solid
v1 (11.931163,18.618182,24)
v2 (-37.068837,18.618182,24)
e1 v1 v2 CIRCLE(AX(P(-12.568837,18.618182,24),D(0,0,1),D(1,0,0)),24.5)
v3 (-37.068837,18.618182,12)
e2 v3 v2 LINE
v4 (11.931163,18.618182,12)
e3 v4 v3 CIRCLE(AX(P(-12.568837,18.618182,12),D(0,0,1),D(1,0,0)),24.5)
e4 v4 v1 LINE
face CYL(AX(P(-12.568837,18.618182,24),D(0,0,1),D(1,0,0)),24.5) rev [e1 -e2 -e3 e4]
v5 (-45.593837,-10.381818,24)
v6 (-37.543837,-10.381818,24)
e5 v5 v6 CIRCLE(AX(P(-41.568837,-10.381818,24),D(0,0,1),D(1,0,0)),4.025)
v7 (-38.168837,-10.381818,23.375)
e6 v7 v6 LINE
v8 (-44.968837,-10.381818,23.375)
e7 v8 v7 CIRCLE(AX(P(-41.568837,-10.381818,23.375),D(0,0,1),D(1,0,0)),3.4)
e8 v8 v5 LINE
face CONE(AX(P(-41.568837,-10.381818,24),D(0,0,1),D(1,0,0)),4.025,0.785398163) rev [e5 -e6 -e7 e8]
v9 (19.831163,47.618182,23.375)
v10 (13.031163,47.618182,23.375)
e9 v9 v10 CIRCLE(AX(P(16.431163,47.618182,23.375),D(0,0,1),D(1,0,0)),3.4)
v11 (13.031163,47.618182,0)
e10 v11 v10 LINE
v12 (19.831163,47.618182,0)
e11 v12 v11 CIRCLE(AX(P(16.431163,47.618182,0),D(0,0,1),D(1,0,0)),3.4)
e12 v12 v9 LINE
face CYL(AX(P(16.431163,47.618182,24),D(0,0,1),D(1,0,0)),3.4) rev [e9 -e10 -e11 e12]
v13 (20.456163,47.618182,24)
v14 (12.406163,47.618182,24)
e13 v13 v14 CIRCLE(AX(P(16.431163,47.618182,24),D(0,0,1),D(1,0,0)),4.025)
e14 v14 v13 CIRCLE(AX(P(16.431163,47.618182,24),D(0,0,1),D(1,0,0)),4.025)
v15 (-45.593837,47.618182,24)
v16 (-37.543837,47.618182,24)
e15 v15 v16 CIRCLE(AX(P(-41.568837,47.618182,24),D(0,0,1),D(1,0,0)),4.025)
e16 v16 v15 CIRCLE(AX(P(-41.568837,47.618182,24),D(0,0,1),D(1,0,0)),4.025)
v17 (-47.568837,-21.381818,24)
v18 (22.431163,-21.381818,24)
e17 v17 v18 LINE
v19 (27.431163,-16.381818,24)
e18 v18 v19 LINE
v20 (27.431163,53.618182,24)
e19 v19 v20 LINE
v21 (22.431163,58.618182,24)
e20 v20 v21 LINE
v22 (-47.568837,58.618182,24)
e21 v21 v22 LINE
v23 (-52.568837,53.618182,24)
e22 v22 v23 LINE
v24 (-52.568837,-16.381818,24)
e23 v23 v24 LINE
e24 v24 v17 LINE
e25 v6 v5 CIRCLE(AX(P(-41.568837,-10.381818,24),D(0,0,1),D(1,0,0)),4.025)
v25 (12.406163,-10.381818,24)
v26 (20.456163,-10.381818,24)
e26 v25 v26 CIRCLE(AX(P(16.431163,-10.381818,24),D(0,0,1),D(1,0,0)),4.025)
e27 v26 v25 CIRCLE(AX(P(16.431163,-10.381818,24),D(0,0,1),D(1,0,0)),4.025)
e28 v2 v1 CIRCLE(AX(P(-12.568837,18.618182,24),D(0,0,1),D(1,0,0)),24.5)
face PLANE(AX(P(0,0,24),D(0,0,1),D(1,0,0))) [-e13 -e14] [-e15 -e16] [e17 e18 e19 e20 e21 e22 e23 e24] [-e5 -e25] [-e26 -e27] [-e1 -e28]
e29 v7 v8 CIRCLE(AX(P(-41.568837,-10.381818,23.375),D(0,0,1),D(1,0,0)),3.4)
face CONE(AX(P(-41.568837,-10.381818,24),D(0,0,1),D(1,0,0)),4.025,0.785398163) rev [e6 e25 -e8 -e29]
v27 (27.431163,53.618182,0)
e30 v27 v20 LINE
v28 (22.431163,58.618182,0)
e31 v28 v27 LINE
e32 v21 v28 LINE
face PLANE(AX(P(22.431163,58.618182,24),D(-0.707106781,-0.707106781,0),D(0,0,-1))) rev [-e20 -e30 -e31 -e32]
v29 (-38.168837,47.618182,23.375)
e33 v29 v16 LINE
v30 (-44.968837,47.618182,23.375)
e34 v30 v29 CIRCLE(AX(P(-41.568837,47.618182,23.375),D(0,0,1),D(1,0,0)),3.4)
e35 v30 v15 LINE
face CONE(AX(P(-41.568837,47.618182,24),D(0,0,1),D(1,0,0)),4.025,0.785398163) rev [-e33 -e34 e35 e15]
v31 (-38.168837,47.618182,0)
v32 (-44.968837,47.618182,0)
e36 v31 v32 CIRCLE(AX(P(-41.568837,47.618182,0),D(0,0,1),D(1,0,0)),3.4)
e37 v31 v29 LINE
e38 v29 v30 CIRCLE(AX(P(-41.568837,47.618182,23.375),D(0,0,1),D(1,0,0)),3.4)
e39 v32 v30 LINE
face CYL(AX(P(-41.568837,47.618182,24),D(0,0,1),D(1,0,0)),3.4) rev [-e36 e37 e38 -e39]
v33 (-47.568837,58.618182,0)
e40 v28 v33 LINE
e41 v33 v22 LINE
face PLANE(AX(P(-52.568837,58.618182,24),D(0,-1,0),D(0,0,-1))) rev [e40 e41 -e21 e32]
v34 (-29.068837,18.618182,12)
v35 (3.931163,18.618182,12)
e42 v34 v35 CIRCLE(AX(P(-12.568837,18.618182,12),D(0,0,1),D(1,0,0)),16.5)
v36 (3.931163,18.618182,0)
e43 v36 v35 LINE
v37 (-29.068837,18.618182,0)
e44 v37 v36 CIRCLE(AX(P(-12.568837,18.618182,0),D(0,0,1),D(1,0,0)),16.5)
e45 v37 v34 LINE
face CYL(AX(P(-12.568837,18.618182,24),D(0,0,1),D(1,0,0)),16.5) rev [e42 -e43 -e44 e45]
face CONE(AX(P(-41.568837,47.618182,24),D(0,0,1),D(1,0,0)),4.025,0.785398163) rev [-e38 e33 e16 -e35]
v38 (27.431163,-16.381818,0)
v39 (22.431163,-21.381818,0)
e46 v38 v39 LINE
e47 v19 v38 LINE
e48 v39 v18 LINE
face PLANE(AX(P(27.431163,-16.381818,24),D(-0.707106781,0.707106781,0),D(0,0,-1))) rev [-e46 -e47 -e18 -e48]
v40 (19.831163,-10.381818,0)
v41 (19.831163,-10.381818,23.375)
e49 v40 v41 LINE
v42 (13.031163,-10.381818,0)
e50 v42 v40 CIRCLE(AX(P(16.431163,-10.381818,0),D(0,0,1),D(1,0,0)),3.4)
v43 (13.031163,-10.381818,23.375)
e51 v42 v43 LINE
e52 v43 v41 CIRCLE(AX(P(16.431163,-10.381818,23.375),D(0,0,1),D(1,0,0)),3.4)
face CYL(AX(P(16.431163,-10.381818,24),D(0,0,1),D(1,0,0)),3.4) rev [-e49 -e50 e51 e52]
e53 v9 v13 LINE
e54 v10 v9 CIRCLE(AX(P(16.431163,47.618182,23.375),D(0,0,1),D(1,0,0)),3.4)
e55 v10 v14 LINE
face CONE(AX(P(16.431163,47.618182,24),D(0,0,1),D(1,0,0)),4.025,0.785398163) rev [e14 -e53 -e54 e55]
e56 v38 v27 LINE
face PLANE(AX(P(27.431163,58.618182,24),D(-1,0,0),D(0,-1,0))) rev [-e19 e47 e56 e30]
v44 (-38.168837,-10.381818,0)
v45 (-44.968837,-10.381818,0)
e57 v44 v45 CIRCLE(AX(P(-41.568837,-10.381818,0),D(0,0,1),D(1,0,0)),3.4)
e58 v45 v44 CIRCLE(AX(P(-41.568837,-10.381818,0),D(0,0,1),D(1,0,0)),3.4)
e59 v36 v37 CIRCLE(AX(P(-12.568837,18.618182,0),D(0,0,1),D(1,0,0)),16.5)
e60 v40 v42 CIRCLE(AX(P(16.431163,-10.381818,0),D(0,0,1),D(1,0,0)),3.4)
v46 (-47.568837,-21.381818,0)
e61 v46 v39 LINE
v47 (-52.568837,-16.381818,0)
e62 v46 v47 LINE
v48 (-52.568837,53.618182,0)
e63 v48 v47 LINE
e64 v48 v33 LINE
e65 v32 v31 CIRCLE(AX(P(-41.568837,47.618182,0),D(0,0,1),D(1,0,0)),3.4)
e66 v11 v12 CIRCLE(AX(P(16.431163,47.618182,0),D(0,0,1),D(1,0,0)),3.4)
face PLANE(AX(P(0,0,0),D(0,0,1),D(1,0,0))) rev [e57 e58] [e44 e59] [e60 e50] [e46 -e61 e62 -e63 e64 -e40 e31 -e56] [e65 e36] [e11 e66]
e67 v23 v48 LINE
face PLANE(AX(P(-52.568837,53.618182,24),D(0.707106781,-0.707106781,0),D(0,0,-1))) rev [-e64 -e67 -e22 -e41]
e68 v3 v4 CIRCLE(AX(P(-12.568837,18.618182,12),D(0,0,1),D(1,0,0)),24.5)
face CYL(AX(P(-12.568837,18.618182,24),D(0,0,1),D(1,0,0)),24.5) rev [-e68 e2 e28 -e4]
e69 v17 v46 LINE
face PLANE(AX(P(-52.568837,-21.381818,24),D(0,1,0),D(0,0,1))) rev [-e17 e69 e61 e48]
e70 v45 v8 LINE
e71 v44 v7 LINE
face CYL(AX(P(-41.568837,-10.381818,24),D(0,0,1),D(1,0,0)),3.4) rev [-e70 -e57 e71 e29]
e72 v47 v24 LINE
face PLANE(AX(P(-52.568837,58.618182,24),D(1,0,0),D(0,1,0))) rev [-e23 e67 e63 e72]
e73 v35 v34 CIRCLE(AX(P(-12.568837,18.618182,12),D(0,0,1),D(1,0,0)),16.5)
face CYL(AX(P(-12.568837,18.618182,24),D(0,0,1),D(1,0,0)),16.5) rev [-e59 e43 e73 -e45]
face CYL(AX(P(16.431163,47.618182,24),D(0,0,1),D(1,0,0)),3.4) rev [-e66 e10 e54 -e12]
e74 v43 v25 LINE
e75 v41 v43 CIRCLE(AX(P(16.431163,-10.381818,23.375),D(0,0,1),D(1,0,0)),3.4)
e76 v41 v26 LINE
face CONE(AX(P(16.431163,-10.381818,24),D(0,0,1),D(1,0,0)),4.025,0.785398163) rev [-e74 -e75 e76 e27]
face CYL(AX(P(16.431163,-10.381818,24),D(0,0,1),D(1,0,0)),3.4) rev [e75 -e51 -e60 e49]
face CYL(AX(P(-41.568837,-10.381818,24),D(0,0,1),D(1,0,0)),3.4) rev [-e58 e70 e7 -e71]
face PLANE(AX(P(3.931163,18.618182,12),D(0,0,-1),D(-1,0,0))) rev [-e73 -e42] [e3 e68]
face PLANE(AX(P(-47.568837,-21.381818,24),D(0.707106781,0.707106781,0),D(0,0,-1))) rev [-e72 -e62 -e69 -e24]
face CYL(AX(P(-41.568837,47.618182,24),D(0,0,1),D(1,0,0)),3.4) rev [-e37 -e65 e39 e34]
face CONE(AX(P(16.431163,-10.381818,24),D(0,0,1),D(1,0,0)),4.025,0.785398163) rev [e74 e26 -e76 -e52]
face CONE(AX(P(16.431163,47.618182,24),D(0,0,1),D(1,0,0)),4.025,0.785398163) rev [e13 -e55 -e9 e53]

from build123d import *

# Parameters (mm, degrees)
SKETCH1_W                   = 80
SKETCH1_H                   = 80
BOSS_EXTRUDE1_DEPTH         = 24
HOLE1_D                     = 33
HOLE1_CBORE_D               = 49
HOLE1_CBORE_DEPTH           = 12
M8_TAPPED_HOLE1_D           = 6.8
M8_TAPPED_HOLE1_CSINK_D     = 8.05
M8_TAPPED_HOLE1_CSINK_ANGLE = 90
CHAMFER1_SIZE               = 5


with BuildPart() as part:
    # Sketch1 → Boss-Extrude1 (new body)
    with BuildSketch(Plane.XY):
        with Locations((-12.568836811, 18.618181818)):
            Rectangle(SKETCH1_W, SKETCH1_H)
    extrude(amount=BOSS_EXTRUDE1_DEPTH)

    # Hole1 (through all)
    with Locations(Plane.XY.offset(24)):
        with Locations((-12.568836811, 18.618181818)):
            CounterBoreHole(HOLE1_D / 2, HOLE1_CBORE_D / 2, HOLE1_CBORE_DEPTH)

    # M8 Tapped Hole1 (through all)
    with Locations(Plane.XY.offset(24)):
        with Locations((-41.568836811, 47.618181818), (16.431163189, 47.618181818), (16.431163189, -10.381818182), (-41.568836811, -10.381818182)):
            CounterSinkHole(M8_TAPPED_HOLE1_D / 2, M8_TAPPED_HOLE1_CSINK_D / 2, counter_sink_angle=M8_TAPPED_HOLE1_CSINK_ANGLE)

    # Chamfer1
    chamfer1_edges = [part.edges().sort_by_distance(p)[0] for p in [
        (-52.568836811, 58.618181818, 12),
        (27.431163189, 58.618181818, 12),
        (27.431163189, -21.381818182, 12),
        (-52.568836811, -21.381818182, 12),
    ]]
    chamfer(chamfer1_edges, length=CHAMFER1_SIZE)


solid = part.part
